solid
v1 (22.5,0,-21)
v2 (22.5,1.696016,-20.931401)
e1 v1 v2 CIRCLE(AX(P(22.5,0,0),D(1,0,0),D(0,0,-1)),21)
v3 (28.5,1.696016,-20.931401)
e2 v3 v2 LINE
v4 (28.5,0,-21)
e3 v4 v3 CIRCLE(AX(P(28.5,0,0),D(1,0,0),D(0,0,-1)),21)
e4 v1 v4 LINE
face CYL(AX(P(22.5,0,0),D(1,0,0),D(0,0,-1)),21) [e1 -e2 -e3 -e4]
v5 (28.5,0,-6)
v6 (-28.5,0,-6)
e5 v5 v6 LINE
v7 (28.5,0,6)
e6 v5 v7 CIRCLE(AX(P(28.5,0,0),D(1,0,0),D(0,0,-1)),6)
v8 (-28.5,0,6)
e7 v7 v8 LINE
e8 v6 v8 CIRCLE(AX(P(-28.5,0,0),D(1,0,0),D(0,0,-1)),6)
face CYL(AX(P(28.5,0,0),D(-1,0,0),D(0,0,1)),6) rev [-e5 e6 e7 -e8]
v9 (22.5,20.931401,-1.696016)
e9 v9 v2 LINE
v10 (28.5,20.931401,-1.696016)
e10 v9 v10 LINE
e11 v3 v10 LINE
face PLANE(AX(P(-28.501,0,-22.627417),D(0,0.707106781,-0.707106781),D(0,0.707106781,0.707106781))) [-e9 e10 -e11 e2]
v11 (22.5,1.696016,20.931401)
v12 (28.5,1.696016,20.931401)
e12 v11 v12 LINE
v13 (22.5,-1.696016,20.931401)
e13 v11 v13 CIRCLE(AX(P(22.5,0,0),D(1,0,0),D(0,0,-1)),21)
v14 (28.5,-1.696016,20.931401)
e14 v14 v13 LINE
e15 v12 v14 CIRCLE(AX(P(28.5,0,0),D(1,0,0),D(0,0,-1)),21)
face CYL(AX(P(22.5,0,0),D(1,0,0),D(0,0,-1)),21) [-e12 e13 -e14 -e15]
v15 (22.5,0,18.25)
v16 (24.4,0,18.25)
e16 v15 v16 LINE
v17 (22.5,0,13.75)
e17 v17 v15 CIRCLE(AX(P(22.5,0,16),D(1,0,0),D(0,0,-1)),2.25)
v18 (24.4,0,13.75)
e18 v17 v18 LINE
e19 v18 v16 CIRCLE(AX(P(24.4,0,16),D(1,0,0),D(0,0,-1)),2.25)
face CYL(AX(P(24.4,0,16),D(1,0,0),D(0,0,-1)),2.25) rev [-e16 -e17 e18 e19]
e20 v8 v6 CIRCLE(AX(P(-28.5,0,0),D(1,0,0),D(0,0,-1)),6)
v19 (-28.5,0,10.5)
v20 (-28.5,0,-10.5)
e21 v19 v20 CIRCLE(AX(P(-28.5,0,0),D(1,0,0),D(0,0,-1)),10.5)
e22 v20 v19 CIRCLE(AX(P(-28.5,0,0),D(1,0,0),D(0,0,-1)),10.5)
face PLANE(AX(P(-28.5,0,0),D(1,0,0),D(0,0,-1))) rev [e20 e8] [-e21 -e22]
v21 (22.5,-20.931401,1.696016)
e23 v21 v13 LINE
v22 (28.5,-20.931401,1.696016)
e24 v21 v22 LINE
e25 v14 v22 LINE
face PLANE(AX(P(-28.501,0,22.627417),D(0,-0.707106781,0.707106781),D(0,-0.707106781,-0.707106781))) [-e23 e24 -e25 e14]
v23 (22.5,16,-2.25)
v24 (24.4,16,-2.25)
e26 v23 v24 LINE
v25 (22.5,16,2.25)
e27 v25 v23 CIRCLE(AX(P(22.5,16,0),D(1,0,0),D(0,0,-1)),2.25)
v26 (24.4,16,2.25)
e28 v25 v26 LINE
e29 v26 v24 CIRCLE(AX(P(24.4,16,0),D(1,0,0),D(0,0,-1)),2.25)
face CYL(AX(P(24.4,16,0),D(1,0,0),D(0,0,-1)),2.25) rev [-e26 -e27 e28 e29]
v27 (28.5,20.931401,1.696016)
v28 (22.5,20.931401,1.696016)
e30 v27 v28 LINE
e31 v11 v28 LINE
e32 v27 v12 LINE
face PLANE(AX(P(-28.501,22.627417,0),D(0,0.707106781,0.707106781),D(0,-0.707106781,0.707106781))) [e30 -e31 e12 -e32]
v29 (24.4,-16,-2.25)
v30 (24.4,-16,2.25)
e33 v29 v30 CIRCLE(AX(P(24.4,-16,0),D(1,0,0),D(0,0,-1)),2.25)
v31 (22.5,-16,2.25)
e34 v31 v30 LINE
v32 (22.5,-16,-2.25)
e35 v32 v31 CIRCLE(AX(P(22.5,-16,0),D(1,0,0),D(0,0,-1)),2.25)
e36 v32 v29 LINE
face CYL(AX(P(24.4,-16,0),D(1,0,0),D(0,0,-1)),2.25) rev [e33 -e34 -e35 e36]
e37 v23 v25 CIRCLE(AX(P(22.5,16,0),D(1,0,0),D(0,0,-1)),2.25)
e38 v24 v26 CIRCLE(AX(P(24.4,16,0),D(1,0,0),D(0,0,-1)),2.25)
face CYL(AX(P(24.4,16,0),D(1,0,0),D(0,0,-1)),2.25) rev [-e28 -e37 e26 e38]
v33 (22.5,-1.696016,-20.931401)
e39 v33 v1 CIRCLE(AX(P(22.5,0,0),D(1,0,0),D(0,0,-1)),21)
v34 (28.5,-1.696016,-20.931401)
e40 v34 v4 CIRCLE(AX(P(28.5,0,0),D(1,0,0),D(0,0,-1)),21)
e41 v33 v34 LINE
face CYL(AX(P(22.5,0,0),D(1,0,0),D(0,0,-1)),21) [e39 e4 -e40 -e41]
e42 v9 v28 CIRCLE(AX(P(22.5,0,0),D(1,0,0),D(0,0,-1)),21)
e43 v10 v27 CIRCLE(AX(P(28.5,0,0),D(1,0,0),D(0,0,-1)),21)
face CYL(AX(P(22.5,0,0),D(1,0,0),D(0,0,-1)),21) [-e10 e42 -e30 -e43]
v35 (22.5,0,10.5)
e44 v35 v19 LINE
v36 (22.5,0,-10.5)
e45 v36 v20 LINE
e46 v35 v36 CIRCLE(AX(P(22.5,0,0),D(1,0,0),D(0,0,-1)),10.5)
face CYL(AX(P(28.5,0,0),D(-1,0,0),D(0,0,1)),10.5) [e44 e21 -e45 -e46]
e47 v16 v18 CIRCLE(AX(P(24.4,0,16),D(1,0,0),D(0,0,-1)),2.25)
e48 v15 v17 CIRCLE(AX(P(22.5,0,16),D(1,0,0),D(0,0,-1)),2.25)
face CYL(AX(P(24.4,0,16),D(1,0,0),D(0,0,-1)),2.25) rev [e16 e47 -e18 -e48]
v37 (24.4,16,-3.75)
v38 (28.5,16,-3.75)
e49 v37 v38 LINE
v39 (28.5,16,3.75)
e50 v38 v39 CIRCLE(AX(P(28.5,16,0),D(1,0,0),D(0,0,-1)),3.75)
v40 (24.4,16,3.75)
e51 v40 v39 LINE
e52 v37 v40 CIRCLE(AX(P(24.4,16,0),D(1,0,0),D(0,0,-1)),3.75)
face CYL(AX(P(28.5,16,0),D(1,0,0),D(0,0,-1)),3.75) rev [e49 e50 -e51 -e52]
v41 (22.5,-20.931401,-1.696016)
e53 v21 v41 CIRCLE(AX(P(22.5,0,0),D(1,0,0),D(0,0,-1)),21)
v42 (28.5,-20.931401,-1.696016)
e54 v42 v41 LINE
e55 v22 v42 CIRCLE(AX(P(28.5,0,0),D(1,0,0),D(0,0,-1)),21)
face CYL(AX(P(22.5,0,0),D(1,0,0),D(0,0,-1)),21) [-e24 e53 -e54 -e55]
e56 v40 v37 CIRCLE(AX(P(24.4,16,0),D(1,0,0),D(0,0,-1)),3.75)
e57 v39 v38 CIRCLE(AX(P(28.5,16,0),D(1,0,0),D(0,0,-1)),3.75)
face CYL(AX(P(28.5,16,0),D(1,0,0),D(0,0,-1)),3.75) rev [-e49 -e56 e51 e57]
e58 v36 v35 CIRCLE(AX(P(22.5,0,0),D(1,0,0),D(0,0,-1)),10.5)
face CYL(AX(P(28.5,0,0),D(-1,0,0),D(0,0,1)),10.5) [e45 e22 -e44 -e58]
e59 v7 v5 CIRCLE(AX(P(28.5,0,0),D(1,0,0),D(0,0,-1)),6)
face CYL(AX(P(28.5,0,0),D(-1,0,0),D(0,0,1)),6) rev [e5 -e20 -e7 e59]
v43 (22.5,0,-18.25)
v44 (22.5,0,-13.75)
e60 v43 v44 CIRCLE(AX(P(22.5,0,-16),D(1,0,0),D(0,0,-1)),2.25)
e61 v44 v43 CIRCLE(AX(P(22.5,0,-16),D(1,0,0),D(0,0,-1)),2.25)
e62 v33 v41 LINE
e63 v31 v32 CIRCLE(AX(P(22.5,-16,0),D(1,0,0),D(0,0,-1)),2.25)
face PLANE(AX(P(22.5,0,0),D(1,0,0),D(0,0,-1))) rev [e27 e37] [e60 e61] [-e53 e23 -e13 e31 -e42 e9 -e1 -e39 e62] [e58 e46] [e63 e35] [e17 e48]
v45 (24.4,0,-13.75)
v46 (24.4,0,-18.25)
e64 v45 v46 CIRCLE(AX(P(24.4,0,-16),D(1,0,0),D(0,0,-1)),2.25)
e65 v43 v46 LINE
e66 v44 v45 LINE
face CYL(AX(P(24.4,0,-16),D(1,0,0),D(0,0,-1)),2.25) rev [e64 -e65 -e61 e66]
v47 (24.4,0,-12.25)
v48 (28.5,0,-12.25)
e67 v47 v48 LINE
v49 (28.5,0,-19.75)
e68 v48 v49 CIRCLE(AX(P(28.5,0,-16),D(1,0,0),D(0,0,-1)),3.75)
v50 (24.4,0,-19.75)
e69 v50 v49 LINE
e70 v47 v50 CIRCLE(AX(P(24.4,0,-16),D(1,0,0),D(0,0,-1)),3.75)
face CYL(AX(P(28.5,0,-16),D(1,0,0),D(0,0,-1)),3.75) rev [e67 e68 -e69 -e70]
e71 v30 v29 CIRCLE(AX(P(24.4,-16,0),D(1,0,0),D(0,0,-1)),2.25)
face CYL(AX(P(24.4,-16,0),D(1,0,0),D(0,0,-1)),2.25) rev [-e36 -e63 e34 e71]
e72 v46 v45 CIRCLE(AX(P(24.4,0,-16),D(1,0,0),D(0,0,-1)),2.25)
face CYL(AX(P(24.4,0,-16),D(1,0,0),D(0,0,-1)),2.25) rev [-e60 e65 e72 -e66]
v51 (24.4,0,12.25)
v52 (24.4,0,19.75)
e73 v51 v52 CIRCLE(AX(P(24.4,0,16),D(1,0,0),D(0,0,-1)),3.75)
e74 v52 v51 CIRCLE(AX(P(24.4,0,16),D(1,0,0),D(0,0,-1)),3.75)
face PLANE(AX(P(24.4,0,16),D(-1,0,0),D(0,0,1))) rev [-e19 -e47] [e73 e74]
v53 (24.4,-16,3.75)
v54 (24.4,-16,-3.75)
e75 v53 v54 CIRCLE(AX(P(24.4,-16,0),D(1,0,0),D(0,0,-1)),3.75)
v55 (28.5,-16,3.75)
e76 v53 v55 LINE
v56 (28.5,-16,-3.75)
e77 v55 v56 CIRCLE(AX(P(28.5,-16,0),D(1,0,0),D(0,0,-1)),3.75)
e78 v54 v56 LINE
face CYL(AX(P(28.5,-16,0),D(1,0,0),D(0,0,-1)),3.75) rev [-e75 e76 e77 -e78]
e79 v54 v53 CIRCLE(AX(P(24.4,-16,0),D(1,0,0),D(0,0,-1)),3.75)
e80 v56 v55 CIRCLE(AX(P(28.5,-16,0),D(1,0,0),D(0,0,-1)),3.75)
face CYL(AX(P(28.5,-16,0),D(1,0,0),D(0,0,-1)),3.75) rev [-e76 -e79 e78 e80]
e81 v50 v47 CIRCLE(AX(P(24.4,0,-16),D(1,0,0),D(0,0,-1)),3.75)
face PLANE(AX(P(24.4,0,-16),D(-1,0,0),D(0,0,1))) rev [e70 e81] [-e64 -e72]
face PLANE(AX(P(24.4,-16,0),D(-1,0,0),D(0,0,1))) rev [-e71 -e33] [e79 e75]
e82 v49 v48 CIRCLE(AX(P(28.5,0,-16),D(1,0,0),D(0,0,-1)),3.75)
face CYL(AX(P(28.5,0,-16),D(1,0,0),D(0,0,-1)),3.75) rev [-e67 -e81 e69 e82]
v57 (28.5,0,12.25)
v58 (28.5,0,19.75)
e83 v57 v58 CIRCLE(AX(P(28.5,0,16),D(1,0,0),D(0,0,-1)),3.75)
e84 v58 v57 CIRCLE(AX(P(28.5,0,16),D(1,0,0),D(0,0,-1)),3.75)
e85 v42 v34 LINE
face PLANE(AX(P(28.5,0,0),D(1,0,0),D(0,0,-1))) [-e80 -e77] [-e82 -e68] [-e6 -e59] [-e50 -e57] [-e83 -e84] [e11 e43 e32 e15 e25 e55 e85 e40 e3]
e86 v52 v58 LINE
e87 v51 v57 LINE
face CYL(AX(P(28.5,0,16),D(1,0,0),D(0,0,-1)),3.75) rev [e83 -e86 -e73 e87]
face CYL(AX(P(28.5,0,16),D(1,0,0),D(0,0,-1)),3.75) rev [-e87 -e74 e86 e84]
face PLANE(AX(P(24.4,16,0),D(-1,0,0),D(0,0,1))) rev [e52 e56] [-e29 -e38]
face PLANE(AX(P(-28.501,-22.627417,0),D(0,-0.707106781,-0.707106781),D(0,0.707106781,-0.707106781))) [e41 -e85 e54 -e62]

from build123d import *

# Parameters (mm, degrees)
SKETCH1_R                      = 10.5
SKETCH1_R_2                    = 6
BOSS_EXTRUDE1_DEPTH            = 28.5
BOSS_EXTRUDE2_START            = -6
SKETCH2_R                      = 21
SKETCH2_R_2                    = 6
BOSS_EXTRUDE2_DEPTH            = 6
F_7_5_7_5_DIAMETER_HOLE1_D     = 7.5
F_7_5_7_5_DIAMETER_HOLE1_DEPTH = 4.1
F_4_5_4_5_DIAMETER_HOLE1_D     = 4.5
CIRPATTERN1_COUNT              = 4
CUT_EXTRUDE1_START             = -6
SKETCH7_OUTSIDE_W              = 60.464
SKETCH7_OUTSIDE_H              = 60.464
CUT_EXTRUDE1_DEPTH             = 6


with BuildPart() as part:
    # Sketch1 → Boss-Extrude1 (new, symmetric)
    with BuildSketch(Plane(origin=(0, 0, 0), x_dir=(0, 0, -1), z_dir=(1, 0, 0))):
        with Locations(Location((0, 0, 0), (0, 0, 180))):
            Circle(SKETCH1_R)
        with Locations(Location((0, 0, 0), (0, 0, 180))):
            Circle(SKETCH1_R_2, mode=Mode.SUBTRACT)
    extrude(amount=BOSS_EXTRUDE1_DEPTH, both=True)

    # Sketch2 → Boss-Extrude2 (add)
    with BuildSketch(Plane(origin=(28.5, 0, 0), x_dir=(0, 0, -1), z_dir=(1, 0, 0)).offset(BOSS_EXTRUDE2_START)):
        Circle(SKETCH2_R)
        with Locations(Location((0, 0, 0), (0, 0, 180))):
            Circle(SKETCH2_R_2, mode=Mode.SUBTRACT)
    extrude(amount=BOSS_EXTRUDE2_DEPTH)

    # Ø7.5 (7.5) Diameter Hole1
    with Locations(Plane(origin=(28.5, 0, 0), x_dir=(0, 0, -1), z_dir=(1, 0, 0))):
        with Locations((0, 16)):
            f_7_5_7_5_diameter_hole1 = Hole(F_7_5_7_5_DIAMETER_HOLE1_D / 2, depth=F_7_5_7_5_DIAMETER_HOLE1_DEPTH)

    # Ø4.5 (4.5) Diameter Hole1 (through all)
    with Locations(Plane(origin=(24.4, 0, 0), x_dir=(0, 0, -1), z_dir=(1, 0, 0))):
        with Locations((0, 16)):
            f_4_5_4_5_diameter_hole1 = Hole(F_4_5_4_5_DIAMETER_HOLE1_D / 2)

    # CirPattern1: Ø7.5 (7.5) Diameter Hole1, Ø4.5 (4.5) Diameter Hole1 ×4 about axis
    cirpattern1_axis = Axis((0, 0, 0), (1, 0, 0))
    add([f_7_5_7_5_diameter_hole1.rotate(cirpattern1_axis, i * 360 / CIRPATTERN1_COUNT) for i in range(1, CIRPATTERN1_COUNT)], mode=Mode.SUBTRACT)
    add([f_4_5_4_5_diameter_hole1.rotate(cirpattern1_axis, i * 360 / CIRPATTERN1_COUNT) for i in range(1, CIRPATTERN1_COUNT)], mode=Mode.SUBTRACT)

    # Sketch7 outside → Cut-Extrude1 (cut)
    with BuildSketch(Plane(origin=(28.5, 0, 0), x_dir=(0, 0, -1), z_dir=(1, 0, 0)).offset(CUT_EXTRUDE1_START)):
        Rectangle(SKETCH7_OUTSIDE_W, SKETCH7_OUTSIDE_H)
        Polygon((0, 22.627416998), (-22.627416998, 0), (0, -22.627416998), (22.627416998, 0), align=None, mode=Mode.SUBTRACT)
    extrude(amount=CUT_EXTRUDE1_DEPTH, mode=Mode.SUBTRACT)


solid = part.part
